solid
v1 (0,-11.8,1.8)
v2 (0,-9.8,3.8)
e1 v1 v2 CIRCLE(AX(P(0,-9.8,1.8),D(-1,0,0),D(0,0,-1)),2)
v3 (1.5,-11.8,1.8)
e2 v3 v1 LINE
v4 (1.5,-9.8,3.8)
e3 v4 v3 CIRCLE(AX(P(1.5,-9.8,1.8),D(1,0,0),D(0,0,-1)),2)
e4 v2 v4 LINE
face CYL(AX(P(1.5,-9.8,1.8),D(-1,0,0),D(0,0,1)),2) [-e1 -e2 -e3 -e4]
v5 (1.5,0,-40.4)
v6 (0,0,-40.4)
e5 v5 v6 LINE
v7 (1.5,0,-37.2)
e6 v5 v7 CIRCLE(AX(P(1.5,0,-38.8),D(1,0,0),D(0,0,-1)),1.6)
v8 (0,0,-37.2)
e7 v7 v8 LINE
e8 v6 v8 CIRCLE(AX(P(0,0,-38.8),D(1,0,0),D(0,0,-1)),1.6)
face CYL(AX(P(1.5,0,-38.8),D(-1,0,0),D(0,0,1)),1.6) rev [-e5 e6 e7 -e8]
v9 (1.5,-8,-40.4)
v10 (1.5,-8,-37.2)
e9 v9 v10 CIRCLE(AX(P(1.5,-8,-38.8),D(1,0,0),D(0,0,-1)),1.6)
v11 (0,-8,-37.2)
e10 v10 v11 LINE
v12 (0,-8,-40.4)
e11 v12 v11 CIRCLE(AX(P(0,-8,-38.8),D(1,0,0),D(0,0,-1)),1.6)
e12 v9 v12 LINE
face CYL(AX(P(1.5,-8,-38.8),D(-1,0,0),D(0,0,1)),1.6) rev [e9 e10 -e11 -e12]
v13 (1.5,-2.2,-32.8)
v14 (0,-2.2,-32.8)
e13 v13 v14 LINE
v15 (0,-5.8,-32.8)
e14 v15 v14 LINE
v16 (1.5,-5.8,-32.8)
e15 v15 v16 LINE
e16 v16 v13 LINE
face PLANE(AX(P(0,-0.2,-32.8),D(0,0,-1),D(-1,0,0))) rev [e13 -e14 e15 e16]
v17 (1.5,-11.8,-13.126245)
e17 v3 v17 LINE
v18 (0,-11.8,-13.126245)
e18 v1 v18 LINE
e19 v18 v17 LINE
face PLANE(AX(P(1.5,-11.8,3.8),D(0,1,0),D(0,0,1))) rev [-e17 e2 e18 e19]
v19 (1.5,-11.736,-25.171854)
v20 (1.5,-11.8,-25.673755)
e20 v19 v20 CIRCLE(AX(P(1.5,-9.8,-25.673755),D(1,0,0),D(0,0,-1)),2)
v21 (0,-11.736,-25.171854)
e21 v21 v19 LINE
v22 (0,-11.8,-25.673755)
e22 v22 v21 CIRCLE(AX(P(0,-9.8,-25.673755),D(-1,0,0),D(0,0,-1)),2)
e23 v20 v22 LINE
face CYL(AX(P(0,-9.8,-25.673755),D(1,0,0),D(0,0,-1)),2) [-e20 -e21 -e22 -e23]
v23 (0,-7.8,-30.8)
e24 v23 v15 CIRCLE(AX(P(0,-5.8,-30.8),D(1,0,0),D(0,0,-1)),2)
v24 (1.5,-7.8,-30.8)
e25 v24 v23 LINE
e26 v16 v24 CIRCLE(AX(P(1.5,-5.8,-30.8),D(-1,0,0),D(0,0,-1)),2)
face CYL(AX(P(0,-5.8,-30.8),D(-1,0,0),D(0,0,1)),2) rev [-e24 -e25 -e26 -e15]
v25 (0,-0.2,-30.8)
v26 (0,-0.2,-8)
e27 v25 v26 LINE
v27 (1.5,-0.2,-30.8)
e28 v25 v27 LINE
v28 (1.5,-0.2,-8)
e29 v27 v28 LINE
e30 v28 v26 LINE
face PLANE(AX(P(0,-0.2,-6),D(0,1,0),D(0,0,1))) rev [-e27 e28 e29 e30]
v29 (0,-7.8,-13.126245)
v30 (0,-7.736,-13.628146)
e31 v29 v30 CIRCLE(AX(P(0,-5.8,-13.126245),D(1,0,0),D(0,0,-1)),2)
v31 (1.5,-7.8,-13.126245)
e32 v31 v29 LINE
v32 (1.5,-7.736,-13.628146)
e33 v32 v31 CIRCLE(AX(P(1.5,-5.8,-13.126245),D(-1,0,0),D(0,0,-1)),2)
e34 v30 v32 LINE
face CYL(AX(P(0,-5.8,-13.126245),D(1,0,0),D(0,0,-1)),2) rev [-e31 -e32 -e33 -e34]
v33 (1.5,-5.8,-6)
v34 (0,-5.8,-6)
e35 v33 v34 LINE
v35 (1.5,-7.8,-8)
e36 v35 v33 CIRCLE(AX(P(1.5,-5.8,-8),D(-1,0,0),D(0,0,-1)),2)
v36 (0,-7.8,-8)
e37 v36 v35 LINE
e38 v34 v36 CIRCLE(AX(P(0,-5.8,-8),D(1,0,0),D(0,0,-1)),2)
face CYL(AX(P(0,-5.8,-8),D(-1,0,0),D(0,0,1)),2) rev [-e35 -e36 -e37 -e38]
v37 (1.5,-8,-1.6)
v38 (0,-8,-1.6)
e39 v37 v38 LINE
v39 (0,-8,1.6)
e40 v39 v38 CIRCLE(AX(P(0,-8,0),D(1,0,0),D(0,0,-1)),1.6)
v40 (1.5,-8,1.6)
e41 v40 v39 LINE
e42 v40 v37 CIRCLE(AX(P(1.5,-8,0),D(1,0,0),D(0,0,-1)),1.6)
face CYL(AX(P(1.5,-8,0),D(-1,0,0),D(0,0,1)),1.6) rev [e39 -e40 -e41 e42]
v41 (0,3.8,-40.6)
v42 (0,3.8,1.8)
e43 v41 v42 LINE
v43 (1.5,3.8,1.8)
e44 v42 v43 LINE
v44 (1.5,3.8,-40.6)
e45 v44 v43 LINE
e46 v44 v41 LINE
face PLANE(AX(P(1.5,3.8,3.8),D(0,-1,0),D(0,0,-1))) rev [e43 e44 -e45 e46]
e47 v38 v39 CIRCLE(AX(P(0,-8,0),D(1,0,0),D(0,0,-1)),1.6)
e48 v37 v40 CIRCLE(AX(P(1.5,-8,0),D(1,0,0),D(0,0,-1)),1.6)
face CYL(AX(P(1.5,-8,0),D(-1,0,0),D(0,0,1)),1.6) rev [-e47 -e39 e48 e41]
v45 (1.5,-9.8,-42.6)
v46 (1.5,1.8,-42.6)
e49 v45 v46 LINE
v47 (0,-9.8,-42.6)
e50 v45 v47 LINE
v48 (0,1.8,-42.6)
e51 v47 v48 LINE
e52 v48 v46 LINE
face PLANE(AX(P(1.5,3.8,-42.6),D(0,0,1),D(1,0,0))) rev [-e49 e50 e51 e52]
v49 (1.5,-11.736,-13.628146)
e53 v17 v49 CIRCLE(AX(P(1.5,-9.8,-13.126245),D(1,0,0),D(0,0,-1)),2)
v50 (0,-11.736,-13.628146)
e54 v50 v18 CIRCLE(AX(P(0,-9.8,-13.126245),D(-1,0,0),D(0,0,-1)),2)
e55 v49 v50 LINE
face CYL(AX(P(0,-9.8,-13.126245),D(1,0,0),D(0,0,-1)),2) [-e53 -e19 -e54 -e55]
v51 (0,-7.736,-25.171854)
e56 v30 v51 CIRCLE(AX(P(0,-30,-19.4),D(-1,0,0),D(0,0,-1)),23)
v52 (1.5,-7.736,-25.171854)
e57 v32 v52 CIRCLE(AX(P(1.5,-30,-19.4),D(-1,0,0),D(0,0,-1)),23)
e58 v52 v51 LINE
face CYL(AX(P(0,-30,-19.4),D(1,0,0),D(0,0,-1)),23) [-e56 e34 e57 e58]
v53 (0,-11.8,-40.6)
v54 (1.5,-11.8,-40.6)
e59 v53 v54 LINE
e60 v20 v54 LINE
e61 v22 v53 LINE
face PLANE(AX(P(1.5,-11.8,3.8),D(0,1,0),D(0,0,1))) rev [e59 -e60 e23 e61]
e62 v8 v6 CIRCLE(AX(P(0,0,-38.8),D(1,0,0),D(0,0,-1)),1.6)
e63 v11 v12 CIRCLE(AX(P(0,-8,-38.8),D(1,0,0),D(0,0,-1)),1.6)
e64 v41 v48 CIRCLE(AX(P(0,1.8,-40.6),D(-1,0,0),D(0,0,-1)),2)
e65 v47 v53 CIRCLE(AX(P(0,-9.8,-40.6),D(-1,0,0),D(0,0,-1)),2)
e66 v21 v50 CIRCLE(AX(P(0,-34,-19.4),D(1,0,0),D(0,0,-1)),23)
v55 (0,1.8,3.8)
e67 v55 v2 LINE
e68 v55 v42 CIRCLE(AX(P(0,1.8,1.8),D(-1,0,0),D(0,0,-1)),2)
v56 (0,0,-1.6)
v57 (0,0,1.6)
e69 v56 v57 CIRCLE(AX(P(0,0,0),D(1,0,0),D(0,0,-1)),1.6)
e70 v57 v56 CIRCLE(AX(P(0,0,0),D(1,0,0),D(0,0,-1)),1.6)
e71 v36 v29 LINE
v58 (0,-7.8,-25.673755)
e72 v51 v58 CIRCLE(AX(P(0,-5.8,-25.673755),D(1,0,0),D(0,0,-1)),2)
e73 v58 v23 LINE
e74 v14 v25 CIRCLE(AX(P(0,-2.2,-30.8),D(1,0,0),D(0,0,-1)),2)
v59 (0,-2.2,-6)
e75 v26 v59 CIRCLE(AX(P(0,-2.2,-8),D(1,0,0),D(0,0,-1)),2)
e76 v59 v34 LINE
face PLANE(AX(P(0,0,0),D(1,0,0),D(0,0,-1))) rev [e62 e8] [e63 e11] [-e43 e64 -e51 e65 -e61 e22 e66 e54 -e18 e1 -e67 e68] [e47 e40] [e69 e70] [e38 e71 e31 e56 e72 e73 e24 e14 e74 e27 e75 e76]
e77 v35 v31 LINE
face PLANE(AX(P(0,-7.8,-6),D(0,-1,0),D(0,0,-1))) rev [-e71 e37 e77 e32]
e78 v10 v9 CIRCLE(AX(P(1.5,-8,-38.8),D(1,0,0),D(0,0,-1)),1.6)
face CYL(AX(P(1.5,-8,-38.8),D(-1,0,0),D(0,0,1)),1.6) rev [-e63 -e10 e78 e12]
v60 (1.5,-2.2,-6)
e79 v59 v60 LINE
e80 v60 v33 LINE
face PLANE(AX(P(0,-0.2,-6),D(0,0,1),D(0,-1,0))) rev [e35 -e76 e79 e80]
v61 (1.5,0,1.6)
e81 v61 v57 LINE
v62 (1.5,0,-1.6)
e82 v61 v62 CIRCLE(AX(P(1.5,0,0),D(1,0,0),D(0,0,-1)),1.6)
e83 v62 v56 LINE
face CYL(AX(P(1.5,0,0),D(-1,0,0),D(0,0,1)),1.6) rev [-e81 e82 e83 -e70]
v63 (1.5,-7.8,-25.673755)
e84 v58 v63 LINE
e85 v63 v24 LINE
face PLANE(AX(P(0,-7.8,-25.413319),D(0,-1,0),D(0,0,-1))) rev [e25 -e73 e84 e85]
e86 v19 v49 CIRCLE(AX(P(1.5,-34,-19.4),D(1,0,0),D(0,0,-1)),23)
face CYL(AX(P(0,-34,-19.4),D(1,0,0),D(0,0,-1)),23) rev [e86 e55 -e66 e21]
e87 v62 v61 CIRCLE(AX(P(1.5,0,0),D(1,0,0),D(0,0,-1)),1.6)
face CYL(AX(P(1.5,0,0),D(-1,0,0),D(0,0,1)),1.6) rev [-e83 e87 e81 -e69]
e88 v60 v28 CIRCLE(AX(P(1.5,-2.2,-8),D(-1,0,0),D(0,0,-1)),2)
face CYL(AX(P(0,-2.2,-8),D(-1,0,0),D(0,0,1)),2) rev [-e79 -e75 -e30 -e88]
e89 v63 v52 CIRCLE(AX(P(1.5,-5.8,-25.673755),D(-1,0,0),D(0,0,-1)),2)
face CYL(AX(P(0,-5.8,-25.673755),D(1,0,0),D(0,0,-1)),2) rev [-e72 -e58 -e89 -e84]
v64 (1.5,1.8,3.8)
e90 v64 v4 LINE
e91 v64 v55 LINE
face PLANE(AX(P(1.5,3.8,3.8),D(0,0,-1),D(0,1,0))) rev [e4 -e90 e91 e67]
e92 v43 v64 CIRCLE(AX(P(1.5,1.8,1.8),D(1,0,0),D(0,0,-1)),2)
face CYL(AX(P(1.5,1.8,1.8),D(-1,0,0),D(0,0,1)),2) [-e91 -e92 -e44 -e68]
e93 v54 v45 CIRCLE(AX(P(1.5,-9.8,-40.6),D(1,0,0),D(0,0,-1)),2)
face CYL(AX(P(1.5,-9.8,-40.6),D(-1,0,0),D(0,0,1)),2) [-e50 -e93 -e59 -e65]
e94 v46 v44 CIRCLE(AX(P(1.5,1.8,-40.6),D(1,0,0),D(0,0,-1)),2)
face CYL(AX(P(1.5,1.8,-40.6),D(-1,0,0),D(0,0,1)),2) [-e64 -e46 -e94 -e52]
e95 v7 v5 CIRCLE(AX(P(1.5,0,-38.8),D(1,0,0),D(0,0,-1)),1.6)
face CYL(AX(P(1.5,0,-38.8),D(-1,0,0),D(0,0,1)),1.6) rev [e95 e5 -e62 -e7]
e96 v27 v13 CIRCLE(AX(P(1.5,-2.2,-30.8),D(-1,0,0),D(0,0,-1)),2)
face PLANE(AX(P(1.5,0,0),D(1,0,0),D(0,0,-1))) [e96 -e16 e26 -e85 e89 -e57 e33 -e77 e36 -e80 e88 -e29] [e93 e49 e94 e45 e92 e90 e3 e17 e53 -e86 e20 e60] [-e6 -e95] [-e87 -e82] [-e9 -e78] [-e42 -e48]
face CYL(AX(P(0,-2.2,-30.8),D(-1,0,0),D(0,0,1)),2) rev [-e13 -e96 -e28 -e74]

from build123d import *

# Parameters (mm, degrees)
SKETCH_1_W          = 46.4
SKETCH_1_H          = 15.6
SKETCH_1_R          = 1.6
EXTRUDE_1_DEPTH     = 1.5
SKETCH_2_R          = 23
CUT_EXTRUDE_1_DEPTH = 45.229515032
CUT_EXTRUDE_2_DEPTH = 45.229515032
FILLET_1_R          = 2


with BuildPart() as part:
    # 草图1 → 凸台-拉伸1 (new body)
    with BuildSketch(Plane(origin=(0, 0, 0), x_dir=(0, 0, -1), z_dir=(1, 0, 0))):
        with Locations((19.4, -4)):
            Rectangle(SKETCH_1_W, SKETCH_1_H)
        Circle(SKETCH_1_R, mode=Mode.SUBTRACT)
        with Locations((0, -8)):
            Circle(SKETCH_1_R, mode=Mode.SUBTRACT)
        with Locations((38.8, 0)):
            Circle(SKETCH_1_R, mode=Mode.SUBTRACT)
        with Locations((38.8, -8)):
            Circle(SKETCH_1_R, mode=Mode.SUBTRACT)
    extrude(amount=EXTRUDE_1_DEPTH)

    # 草图2 → 切除-拉伸1 (cut, through all)
    with BuildSketch(Plane(origin=(1.5, 0, 0), x_dir=(0, 0, -1), z_dir=(1, 0, 0))):
        with Locations((19.4, -34)):
            Circle(SKETCH_2_R)
    extrude(amount=-CUT_EXTRUDE_1_DEPTH, mode=Mode.SUBTRACT)

    # 草图3 → 切除-拉伸2 (cut, through all)
    with BuildSketch(Plane(origin=(1.5, 0, 0), x_dir=(0, 0, -1), z_dir=(1, 0, 0))):
        with BuildLine():
            Line((6, -0.2), (32.8, -0.2))
            Line((32.8, -0.2), (32.8, -7.8))
            Line((32.8, -7.8), (25.413318551, -7.8))
            ThreePointArc((25.413318551, -7.8), (19.4, -7), (13.386681449, -7.8))
            Line((13.386681449, -7.8), (6, -7.8))
            Line((6, -7.8), (6, -0.2))
        make_face()
    extrude(amount=-CUT_EXTRUDE_2_DEPTH, mode=Mode.SUBTRACT)

    # 圆角1
    fillet_1_edges = [part.edges().sort_by_distance(p)[0] for p in [
        (0.75, -11.8, -25.413318551),
        (0.75, -11.8, -13.386681449),
        (0.75, -7.8, -6),
        (0.75, -0.2, -6),
        (0.75, -0.2, -32.8),
        (0.75, -7.8, -32.8),
        (0.75, -7.8, -25.413318551),
        (0.75, -7.8, -13.386681449),
        (0.75, 3.8, 3.8),
        (0.75, 3.8, -42.6),
        (0.75, -11.8, -42.6),
        (0.75, -11.8, 3.8),
    ]]
    fillet(fillet_1_edges, radius=FILLET_1_R)


solid = part.part
